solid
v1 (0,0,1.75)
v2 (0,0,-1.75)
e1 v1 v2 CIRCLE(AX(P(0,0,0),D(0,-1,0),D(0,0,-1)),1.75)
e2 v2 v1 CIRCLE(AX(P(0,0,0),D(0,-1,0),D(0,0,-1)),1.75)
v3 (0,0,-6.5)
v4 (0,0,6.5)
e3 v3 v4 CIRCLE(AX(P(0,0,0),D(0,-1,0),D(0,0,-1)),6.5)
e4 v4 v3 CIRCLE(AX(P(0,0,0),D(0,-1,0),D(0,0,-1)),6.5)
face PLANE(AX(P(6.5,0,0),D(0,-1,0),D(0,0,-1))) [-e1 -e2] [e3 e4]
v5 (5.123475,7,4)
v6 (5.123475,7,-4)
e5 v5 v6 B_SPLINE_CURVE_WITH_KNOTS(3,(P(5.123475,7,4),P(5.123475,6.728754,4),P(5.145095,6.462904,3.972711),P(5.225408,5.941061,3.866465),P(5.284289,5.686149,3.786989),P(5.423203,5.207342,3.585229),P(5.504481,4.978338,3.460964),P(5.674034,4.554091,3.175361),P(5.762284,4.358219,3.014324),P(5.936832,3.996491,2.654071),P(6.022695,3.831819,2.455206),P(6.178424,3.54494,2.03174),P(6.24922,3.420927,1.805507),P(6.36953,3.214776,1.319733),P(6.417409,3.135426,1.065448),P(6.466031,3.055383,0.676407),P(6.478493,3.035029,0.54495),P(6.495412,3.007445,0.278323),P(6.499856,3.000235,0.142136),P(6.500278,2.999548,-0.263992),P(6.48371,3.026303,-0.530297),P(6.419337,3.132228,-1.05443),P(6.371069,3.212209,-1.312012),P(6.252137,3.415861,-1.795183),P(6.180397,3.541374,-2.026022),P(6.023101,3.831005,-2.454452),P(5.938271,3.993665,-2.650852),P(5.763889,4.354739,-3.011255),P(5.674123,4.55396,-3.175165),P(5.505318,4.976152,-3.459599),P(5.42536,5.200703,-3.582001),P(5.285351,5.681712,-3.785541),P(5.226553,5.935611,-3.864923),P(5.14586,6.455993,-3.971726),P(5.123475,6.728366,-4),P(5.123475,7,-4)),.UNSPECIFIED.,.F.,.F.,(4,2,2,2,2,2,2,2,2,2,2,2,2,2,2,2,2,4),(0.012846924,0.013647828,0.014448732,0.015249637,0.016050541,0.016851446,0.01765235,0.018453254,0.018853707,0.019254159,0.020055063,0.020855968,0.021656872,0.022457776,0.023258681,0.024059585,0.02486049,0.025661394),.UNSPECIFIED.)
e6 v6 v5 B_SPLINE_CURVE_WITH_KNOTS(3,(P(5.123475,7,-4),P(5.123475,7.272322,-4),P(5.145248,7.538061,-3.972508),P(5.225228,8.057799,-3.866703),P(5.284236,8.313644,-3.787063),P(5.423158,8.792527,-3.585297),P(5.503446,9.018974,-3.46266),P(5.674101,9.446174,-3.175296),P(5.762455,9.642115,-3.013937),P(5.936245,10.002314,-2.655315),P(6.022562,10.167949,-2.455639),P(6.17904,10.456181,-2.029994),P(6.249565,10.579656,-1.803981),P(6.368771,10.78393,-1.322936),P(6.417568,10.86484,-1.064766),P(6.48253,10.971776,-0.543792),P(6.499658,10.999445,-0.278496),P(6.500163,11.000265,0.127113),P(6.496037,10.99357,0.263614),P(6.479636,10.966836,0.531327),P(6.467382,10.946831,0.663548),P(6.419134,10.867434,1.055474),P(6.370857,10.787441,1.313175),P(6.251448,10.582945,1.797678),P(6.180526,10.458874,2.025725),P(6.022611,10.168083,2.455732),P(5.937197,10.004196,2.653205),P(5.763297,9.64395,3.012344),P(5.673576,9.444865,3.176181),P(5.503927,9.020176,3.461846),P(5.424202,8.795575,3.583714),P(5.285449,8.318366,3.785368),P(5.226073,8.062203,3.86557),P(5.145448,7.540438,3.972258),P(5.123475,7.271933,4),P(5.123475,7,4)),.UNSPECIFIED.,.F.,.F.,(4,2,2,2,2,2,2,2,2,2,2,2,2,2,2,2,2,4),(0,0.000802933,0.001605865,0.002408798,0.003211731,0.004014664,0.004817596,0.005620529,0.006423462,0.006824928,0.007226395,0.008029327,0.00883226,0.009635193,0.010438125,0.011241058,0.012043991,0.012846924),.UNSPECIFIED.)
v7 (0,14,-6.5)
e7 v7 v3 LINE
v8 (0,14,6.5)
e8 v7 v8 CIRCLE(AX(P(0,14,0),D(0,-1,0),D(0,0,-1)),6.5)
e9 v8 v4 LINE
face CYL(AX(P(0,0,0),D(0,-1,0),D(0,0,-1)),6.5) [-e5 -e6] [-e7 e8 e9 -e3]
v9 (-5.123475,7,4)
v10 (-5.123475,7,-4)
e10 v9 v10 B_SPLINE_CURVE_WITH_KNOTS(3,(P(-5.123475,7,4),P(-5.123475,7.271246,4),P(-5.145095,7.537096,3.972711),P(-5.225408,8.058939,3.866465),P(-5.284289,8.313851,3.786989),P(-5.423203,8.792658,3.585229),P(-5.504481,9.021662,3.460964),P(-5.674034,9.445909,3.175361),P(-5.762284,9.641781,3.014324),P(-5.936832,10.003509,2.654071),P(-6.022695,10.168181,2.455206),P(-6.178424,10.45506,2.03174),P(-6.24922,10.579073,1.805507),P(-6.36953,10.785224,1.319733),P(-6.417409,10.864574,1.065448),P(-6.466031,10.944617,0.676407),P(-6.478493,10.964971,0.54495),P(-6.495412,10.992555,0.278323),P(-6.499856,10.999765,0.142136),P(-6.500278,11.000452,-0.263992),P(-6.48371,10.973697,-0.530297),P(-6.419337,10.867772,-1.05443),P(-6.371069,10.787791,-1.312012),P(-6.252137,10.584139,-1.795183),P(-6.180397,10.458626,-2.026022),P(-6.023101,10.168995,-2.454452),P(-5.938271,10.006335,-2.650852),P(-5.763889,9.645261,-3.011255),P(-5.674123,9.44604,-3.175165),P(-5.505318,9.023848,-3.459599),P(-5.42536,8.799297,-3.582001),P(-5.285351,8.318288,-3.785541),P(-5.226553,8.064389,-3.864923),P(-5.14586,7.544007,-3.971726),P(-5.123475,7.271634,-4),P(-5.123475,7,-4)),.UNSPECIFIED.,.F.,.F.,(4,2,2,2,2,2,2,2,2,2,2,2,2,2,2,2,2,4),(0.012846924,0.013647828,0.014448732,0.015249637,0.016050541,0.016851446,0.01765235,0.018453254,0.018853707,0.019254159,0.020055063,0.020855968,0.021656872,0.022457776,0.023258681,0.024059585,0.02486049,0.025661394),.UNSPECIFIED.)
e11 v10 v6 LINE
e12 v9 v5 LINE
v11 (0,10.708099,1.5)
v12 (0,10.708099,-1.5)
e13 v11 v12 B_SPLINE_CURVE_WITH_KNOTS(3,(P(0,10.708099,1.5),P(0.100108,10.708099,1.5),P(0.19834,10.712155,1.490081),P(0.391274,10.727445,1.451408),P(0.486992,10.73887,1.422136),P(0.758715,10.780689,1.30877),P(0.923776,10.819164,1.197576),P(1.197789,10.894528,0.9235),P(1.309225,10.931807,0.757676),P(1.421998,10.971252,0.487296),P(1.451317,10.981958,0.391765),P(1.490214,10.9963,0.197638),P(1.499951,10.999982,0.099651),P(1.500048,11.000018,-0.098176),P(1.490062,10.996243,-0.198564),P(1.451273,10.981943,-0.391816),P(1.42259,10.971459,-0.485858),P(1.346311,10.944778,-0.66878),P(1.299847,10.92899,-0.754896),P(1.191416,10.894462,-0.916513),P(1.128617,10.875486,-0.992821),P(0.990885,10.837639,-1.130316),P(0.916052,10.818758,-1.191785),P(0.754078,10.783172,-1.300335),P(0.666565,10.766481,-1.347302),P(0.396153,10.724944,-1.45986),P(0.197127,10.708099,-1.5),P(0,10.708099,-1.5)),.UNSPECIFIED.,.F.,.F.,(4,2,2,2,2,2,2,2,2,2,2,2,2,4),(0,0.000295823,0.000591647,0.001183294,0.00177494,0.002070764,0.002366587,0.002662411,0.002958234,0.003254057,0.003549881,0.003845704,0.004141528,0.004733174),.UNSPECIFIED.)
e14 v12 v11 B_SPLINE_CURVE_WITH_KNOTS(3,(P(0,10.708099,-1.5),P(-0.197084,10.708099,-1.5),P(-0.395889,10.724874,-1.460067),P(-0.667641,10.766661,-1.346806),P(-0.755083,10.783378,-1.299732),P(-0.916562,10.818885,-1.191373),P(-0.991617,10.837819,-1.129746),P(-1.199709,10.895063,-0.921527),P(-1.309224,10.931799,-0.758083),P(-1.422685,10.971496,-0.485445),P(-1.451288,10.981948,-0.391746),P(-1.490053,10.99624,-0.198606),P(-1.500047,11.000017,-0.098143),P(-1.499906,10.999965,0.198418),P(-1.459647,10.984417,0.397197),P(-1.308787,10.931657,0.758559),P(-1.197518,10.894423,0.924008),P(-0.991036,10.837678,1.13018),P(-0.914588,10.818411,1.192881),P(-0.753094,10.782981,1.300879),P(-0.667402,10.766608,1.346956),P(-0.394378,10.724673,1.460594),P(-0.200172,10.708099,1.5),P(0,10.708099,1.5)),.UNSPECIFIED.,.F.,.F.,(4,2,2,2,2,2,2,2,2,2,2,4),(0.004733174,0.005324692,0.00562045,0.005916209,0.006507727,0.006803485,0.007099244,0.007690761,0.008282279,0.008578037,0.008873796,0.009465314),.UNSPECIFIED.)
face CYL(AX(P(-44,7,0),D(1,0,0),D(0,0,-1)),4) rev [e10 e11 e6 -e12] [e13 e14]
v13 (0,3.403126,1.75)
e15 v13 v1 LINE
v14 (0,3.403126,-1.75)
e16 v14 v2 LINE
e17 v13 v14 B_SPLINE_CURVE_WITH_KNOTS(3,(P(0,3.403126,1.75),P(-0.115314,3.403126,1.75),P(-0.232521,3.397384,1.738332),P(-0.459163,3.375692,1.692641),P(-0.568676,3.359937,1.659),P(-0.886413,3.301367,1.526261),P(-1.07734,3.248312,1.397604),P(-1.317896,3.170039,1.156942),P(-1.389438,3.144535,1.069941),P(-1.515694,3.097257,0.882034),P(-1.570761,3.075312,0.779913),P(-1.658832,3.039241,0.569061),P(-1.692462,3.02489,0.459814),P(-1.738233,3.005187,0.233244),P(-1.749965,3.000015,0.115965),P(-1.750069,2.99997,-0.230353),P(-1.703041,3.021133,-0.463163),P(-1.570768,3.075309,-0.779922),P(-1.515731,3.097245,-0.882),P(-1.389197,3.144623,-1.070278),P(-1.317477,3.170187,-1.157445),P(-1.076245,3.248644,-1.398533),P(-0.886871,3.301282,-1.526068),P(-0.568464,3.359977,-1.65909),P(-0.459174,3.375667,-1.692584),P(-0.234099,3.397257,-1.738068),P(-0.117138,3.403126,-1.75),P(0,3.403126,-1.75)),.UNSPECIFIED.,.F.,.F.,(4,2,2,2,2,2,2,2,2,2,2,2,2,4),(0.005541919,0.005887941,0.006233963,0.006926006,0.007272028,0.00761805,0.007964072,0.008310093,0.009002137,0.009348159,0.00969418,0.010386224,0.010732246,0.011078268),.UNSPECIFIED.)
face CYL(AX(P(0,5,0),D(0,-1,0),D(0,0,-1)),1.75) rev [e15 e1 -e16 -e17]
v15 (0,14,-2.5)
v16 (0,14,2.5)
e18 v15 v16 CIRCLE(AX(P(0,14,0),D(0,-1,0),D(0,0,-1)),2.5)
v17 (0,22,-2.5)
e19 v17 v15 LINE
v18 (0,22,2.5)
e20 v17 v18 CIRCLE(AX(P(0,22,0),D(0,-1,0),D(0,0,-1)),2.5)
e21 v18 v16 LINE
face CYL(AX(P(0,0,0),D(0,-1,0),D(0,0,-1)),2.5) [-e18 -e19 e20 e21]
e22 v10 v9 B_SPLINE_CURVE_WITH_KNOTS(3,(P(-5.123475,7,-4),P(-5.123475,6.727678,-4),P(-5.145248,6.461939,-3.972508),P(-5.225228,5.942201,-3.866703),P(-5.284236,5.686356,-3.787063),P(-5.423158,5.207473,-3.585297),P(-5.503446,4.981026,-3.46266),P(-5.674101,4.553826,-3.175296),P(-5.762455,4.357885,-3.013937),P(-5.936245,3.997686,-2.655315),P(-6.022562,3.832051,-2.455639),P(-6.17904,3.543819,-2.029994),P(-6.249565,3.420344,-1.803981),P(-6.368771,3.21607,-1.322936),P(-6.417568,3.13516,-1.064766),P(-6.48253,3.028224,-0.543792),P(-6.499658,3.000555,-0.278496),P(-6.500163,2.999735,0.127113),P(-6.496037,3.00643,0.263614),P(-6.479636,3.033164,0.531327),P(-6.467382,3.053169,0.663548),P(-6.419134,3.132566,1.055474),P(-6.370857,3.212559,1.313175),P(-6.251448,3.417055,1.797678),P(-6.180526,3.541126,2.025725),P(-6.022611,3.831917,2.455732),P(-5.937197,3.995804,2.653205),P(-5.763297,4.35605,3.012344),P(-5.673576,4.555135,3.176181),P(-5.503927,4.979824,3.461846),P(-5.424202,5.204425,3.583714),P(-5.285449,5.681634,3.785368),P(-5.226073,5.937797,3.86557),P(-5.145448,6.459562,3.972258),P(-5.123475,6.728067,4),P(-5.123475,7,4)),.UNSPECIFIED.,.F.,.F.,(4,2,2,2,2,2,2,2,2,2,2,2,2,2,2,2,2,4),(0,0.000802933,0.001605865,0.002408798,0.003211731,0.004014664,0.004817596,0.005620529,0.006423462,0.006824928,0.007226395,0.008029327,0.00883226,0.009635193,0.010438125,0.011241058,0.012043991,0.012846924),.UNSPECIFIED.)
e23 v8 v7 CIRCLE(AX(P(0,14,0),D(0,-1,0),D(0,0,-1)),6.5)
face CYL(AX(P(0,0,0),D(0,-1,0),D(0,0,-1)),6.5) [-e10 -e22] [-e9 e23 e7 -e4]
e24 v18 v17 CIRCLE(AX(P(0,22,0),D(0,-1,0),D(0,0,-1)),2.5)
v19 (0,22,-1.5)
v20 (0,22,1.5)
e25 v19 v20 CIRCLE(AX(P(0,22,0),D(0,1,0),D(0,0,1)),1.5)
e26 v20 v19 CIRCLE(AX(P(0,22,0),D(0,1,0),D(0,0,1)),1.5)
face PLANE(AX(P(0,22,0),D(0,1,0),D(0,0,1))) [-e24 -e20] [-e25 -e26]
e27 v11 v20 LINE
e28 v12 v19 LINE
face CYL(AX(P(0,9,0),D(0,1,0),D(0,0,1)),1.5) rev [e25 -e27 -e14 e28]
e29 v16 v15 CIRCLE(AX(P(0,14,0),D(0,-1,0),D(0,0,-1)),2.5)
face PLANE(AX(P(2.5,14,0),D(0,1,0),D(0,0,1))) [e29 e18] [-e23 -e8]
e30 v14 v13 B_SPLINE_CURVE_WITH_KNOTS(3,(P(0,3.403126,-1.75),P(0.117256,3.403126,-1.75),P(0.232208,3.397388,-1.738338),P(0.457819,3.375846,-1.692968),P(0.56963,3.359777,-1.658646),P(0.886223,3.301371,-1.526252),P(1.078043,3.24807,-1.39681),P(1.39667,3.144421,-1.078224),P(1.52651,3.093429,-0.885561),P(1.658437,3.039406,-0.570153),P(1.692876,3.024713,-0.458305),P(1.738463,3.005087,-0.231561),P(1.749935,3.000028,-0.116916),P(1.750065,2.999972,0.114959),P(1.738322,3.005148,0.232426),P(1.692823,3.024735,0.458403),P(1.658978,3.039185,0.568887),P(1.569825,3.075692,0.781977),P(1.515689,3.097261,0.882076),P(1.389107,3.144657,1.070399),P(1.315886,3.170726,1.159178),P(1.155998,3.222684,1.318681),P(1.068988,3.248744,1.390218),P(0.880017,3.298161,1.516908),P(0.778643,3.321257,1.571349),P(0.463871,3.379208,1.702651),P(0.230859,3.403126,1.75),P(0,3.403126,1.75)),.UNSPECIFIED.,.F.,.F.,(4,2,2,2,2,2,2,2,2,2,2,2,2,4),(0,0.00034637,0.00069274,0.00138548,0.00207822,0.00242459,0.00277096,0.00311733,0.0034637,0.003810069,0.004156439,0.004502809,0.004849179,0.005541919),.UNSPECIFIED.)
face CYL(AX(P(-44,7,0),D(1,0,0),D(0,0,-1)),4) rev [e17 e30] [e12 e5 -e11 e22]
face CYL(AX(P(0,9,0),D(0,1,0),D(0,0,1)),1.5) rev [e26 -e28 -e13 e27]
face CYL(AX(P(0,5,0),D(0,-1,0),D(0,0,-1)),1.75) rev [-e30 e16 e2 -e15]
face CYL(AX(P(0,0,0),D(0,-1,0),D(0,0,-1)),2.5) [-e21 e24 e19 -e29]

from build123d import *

# Parameters (mm, degrees)
CROSS_HOLE_SKETCH_R     = 4
CROSS_HOLE_8_DEPTH      = 44
NIPPLE_POCKET_SKETCH_R  = 1.75
NIPPLE_POCKET_3_5_DEPTH = 5
CABLE_BORE_SKETCH_R     = 1.5
CABLE_BORE_3_DEPTH      = 13


with BuildPart() as part:
    # Barrel Profile Sketch → Barrel Body Revolve (revolve)
    with BuildSketch(Plane.XY, mode=Mode.PRIVATE) as barrel_body_revolve_sk:
        Polygon((0, 0), (0, 22), (2.5, 22), (2.5, 14), (6.5, 14), (6.5, 0), align=None)
    revolve(barrel_body_revolve_sk.sketch.rotate(Axis((0, 0, 0), (0, 1, 0)), 90), axis=Axis((0, 0, 0), (0, 1, 0)))

    # Cross Hole Sketch → Cross Hole Ø8 (cut, symmetric)
    with BuildSketch(Plane(origin=(0, 0, 0), x_dir=(0, 0, -1), z_dir=(1, 0, 0))):
        with Locations((0, 7)):
            Circle(CROSS_HOLE_SKETCH_R)
    extrude(amount=CROSS_HOLE_8_DEPTH, both=True, mode=Mode.SUBTRACT)

    # Nipple Pocket Sketch → Nipple Pocket Ø3.5 (cut)
    with BuildSketch(Plane.XZ):
        with Locations(Location((0, 0, 0), (0, 0, 270))):
            Circle(NIPPLE_POCKET_SKETCH_R)
    extrude(amount=-NIPPLE_POCKET_3_5_DEPTH, mode=Mode.SUBTRACT)

    # Cable Bore Sketch → Cable Bore Ø3 (cut)
    with BuildSketch(Plane(origin=(0, 22, 0), x_dir=(1, 0, 0), z_dir=(0, 1, 0))):
        with Locations(Location((0, 0, 0), (0, 0, 270))):
            Circle(CABLE_BORE_SKETCH_R)
    extrude(amount=-CABLE_BORE_3_DEPTH, mode=Mode.SUBTRACT)


solid = part.part
